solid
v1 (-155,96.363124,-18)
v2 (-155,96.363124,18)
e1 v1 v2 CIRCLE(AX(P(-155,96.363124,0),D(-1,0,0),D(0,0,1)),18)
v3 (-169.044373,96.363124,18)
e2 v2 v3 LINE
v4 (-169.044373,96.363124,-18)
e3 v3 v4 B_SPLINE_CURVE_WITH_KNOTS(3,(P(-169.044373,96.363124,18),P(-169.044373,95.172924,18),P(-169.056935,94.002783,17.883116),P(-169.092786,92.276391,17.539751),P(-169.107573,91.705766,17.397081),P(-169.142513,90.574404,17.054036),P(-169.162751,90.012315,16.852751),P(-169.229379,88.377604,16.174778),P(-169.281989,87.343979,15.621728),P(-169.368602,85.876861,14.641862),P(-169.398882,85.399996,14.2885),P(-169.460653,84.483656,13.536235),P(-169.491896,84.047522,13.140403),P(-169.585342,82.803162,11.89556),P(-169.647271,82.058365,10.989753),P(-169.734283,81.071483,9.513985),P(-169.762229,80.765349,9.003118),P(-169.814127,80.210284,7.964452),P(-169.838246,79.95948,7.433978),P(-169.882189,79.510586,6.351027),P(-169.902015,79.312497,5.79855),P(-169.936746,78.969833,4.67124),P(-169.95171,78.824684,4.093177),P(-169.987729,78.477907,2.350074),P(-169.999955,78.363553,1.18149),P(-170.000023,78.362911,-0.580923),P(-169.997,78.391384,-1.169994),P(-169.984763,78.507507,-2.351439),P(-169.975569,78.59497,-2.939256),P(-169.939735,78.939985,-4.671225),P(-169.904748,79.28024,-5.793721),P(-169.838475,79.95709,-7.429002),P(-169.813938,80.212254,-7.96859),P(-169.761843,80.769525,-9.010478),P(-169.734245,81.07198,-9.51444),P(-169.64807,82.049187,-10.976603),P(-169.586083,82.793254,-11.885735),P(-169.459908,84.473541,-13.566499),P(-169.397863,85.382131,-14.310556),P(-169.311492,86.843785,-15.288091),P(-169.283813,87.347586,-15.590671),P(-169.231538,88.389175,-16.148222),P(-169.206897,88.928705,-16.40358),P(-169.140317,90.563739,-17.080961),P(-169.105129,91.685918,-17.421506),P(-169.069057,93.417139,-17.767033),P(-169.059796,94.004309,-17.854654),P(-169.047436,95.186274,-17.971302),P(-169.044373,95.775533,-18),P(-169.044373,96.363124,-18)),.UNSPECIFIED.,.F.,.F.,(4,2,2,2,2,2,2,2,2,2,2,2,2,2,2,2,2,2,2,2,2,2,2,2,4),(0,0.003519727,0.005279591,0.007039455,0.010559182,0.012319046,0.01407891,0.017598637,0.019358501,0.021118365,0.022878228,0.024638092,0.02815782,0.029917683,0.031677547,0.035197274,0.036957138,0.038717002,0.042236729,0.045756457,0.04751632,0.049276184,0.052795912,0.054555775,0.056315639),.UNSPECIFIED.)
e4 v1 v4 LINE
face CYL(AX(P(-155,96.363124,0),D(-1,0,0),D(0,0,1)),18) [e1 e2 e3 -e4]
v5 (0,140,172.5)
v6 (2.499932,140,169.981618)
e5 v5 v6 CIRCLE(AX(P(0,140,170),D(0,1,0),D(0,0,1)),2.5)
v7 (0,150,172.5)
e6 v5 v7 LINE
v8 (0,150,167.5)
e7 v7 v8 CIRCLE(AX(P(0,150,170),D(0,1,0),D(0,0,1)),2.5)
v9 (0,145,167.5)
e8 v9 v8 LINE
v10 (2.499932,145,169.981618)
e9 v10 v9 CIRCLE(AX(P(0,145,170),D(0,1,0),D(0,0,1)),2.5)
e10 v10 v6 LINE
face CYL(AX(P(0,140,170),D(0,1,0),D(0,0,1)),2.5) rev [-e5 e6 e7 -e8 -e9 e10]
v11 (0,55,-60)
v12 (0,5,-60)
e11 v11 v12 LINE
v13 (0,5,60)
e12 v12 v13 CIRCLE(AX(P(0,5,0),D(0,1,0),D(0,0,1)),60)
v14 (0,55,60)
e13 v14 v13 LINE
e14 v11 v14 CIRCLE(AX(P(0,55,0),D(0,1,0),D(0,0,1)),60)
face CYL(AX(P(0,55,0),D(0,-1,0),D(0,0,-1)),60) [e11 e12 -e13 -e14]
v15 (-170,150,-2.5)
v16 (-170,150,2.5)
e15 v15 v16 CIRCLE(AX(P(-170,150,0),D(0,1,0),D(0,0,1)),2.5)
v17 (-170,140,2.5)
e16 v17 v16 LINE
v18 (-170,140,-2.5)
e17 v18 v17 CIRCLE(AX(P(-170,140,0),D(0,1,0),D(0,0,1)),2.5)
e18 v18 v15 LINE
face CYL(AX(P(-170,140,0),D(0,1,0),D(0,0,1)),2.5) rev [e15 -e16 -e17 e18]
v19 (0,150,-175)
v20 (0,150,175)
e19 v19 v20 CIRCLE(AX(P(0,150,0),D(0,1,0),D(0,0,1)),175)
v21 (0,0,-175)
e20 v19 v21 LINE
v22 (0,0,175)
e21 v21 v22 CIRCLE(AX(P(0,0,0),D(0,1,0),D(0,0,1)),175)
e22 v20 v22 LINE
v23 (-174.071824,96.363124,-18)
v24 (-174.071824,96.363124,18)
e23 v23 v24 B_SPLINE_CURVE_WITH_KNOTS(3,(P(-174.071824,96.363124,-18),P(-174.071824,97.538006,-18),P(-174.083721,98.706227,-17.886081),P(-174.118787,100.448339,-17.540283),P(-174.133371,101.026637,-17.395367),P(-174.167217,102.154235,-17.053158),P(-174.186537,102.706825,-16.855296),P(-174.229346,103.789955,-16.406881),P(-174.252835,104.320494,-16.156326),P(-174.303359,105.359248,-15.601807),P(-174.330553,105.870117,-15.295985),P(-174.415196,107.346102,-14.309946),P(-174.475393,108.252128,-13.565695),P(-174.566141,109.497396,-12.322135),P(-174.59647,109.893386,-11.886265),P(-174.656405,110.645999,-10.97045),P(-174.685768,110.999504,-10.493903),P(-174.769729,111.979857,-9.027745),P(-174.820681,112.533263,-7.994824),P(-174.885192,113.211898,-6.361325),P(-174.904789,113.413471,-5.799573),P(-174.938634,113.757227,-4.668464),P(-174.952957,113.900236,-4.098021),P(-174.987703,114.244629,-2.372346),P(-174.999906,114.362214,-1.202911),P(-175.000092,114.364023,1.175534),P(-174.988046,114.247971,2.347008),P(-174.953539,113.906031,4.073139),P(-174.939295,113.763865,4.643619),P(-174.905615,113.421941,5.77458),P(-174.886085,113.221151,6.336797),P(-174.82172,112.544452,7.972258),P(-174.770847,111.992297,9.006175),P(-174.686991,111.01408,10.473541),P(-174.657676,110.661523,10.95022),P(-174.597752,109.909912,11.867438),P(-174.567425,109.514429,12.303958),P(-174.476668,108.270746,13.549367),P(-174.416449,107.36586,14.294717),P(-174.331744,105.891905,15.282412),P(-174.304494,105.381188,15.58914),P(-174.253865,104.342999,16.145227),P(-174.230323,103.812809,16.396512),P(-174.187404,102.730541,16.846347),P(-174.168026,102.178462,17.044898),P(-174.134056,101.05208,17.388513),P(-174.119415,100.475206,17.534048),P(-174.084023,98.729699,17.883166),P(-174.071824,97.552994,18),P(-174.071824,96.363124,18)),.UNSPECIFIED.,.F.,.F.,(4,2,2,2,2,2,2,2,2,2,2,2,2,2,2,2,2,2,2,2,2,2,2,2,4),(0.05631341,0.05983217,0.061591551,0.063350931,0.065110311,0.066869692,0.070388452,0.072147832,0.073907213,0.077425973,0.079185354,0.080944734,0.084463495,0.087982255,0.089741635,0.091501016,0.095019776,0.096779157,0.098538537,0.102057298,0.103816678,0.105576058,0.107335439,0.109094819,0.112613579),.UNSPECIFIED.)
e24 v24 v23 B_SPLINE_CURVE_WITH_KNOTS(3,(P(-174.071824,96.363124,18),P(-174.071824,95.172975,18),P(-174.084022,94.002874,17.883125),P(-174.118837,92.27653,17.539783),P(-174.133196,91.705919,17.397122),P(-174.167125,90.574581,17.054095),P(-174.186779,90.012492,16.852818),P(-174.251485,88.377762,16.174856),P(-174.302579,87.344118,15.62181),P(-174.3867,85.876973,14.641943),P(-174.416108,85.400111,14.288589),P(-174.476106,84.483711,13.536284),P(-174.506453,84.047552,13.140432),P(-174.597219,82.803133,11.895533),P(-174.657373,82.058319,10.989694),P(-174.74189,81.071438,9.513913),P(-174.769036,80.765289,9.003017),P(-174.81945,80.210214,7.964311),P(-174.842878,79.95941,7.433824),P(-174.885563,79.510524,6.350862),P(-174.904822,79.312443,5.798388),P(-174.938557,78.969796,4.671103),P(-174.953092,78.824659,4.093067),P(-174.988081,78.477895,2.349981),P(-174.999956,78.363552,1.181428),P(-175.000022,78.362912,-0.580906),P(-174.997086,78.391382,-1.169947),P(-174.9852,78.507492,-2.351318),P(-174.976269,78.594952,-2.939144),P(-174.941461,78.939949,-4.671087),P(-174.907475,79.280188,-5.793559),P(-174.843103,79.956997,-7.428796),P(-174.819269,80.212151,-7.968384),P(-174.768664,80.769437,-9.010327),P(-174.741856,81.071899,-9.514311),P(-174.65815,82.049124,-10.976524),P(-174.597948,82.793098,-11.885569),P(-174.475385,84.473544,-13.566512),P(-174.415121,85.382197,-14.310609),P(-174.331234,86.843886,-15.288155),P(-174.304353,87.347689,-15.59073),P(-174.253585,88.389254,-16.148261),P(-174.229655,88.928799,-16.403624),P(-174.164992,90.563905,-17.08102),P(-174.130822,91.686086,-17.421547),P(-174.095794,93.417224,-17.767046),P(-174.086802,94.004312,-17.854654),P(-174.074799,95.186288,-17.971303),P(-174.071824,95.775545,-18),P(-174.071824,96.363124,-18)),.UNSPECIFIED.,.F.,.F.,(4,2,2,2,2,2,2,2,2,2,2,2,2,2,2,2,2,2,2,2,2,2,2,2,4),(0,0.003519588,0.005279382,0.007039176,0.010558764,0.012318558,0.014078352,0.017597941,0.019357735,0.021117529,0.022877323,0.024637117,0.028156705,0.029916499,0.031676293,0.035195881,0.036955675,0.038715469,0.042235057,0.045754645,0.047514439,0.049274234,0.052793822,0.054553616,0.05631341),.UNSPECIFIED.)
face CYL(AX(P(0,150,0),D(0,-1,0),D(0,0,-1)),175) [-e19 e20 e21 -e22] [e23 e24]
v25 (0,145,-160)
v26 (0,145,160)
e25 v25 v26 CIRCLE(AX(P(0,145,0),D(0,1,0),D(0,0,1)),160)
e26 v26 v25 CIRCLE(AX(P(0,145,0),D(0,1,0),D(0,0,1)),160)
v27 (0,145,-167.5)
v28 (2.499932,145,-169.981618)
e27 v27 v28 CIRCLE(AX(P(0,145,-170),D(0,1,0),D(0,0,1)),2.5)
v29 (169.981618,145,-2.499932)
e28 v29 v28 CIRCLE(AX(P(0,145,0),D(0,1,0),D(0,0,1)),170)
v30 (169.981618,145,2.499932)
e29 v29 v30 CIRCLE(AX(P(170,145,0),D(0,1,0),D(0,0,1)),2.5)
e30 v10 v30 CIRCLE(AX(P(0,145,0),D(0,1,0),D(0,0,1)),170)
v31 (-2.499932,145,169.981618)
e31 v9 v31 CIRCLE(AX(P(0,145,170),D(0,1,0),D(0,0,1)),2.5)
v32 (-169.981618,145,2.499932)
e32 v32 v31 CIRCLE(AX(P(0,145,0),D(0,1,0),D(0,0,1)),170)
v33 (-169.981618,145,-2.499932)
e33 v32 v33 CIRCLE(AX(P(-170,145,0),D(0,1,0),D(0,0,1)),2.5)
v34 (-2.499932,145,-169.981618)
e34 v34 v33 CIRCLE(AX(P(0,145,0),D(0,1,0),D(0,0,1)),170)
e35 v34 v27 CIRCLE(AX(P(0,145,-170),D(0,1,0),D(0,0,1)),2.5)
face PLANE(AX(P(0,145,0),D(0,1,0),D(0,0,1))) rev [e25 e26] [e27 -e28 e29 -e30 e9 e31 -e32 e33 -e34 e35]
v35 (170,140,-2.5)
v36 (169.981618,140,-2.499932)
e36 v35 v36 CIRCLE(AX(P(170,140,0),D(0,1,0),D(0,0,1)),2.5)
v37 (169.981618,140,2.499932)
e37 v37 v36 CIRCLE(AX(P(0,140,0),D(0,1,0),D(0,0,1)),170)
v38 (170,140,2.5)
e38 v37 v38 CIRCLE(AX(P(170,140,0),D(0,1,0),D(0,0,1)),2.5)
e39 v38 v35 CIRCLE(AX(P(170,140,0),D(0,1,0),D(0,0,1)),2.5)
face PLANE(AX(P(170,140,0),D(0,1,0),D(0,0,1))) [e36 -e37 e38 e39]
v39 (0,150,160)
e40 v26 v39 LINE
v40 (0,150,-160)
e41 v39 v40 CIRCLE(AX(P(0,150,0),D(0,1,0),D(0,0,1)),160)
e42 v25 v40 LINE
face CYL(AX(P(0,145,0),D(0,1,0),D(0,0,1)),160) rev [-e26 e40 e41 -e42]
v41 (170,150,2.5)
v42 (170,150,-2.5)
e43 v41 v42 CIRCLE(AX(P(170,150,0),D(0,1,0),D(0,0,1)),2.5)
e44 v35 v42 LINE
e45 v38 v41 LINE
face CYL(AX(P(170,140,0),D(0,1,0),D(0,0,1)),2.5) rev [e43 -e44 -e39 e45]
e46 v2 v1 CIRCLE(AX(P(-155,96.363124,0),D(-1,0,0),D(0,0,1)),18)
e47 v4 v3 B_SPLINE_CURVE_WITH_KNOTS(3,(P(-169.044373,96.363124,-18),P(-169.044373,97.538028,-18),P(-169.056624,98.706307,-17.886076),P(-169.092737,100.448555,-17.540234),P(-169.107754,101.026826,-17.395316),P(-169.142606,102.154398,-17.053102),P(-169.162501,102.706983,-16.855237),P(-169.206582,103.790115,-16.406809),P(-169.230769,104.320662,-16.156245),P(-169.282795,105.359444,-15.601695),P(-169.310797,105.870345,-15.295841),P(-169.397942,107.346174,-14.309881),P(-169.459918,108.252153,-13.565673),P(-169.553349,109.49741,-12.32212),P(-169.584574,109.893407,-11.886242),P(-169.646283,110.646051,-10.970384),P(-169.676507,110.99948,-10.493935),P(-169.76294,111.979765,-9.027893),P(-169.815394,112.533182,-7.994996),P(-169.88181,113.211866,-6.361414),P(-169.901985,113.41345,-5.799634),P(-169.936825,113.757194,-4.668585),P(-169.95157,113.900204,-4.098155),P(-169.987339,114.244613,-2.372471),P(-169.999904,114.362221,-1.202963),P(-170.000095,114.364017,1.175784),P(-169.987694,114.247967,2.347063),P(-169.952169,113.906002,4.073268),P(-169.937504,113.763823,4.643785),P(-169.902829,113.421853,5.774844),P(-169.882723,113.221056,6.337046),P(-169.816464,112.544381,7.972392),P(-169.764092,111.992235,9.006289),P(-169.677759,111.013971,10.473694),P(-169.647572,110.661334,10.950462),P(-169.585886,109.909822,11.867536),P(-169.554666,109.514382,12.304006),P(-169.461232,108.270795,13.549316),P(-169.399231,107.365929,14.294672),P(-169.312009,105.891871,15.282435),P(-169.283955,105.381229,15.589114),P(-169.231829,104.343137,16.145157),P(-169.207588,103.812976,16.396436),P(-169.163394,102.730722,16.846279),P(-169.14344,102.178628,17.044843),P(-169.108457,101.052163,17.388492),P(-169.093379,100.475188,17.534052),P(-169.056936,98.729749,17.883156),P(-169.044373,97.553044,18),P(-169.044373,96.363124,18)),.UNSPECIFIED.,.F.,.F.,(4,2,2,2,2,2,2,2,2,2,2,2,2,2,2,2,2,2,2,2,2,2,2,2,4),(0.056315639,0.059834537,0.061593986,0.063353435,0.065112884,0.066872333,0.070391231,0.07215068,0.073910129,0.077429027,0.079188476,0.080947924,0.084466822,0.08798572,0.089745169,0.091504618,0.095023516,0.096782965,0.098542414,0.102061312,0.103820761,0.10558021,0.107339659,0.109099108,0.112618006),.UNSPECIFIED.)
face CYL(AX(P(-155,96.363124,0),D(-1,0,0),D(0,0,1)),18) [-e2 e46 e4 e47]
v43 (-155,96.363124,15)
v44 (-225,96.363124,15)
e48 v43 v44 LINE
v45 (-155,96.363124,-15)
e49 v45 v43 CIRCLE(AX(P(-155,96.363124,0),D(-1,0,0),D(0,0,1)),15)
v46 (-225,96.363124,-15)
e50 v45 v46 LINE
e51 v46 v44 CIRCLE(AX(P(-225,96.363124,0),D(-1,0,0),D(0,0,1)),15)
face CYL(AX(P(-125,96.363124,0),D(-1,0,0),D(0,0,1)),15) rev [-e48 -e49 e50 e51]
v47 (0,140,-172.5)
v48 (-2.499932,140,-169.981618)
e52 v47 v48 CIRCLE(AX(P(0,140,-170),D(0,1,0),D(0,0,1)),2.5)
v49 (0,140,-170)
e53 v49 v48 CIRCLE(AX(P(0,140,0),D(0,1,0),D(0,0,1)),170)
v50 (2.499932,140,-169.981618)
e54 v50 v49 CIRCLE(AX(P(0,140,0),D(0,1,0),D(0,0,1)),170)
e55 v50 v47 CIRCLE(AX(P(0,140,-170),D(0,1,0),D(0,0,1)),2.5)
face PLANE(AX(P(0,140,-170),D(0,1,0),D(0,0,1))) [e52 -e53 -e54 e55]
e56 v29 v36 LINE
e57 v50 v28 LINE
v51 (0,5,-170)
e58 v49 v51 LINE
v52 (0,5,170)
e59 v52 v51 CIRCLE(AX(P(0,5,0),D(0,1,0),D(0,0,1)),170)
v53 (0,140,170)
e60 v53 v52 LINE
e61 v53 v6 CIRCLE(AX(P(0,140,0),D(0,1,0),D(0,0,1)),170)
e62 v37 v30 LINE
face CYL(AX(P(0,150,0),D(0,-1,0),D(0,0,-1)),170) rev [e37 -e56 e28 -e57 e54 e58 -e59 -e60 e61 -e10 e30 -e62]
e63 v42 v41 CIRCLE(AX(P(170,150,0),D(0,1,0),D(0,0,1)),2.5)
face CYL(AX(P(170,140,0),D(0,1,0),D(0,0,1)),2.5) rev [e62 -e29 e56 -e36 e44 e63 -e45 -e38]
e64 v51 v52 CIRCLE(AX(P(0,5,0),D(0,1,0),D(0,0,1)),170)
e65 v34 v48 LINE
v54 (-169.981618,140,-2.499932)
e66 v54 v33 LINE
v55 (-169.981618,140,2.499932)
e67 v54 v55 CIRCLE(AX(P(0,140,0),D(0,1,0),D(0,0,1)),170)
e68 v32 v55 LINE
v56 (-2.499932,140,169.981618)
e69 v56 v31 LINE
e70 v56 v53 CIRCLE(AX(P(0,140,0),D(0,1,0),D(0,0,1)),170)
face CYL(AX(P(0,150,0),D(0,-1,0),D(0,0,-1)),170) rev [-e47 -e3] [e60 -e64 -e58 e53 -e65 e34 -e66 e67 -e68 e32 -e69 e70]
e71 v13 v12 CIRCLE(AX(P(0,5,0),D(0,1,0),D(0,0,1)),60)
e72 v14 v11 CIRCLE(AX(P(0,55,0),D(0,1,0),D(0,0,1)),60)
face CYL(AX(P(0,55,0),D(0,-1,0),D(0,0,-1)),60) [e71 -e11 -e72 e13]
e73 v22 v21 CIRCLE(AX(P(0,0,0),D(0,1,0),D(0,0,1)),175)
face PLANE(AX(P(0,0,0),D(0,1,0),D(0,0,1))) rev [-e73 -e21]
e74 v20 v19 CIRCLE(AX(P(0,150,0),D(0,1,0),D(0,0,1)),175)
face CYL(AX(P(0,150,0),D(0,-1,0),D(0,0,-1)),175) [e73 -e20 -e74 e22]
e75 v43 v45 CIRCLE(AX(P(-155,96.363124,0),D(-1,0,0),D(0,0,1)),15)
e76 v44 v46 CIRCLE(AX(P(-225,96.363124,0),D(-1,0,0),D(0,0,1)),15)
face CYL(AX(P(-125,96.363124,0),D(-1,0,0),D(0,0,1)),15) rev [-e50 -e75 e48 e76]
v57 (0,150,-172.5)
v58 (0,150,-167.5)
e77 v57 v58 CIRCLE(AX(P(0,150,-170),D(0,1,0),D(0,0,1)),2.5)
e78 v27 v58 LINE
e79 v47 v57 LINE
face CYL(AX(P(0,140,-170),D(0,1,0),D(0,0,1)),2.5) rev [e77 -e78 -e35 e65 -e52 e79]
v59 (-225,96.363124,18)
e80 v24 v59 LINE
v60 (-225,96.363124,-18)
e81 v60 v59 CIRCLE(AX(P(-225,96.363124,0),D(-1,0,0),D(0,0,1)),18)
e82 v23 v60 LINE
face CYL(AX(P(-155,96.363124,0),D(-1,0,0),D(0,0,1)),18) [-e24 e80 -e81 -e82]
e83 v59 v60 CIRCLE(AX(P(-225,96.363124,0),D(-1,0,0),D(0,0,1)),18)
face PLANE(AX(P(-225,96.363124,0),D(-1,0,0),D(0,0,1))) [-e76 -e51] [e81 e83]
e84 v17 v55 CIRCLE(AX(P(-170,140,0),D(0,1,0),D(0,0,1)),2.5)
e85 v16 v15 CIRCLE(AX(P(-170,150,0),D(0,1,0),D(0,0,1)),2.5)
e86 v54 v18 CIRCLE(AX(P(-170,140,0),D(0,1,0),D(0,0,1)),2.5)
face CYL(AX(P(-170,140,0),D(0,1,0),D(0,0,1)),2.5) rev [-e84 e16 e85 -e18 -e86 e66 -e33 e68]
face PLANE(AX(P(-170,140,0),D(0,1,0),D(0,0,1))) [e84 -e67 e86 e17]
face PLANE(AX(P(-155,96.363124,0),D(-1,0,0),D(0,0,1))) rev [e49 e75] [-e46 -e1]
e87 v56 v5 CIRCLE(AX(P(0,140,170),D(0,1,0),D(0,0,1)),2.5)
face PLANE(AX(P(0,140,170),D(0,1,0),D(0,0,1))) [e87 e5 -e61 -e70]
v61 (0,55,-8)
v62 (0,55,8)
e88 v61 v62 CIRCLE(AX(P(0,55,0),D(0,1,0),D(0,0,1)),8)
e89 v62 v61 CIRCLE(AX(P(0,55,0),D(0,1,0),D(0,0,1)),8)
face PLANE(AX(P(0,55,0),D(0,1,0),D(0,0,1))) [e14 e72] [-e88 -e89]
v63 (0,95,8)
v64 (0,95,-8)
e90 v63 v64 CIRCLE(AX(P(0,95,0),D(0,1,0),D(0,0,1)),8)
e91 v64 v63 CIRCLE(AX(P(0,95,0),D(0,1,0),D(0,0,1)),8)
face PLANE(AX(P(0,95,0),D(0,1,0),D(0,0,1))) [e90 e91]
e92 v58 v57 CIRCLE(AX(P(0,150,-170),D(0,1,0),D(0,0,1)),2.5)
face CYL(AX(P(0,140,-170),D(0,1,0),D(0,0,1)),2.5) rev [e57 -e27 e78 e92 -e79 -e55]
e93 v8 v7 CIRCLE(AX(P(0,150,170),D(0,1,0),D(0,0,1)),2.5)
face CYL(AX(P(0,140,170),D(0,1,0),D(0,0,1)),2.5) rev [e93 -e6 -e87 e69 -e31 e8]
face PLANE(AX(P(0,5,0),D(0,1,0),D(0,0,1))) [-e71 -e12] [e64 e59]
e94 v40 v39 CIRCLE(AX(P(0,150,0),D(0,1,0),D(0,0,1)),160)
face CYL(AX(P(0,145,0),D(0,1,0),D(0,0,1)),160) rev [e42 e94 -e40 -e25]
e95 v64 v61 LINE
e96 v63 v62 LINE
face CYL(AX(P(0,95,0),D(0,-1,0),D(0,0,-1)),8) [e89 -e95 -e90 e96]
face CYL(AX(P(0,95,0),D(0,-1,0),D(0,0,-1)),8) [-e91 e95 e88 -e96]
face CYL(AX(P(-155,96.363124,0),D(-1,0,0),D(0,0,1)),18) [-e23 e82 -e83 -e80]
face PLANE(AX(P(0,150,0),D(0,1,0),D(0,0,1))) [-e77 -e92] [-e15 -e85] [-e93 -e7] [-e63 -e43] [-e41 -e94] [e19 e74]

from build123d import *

# Parameters (mm, degrees)
SKETCH1_R                = 175
BOSS_EXTRUDE2_DEPTH      = 150
SHELL2_T                 = -5
SKETCH2_R                = 60
BOSS_EXTRUDE3_DEPTH      = 50
SKETCH_3_3_R             = 15
CUT_EXTRUDE1_DEPTH       = 50
BOSS_EXTRUDE5_DEPTH      = 50
BOSS_EXTRUDE5_DEPTH_BACK = 20
SKETCH_3_3_2_R           = 18
SKETCH_3_3_2_R_2         = 15
SKETCH5_R                = 8
BOSS_EXTRUDE6_DEPTH      = 40
BOSS_EXTRUDE7_START      = -5
SKETCH6_R                = 170
SKETCH6_R_2              = 160
BOSS_EXTRUDE7_DEPTH      = 5
SKETCH7_R                = 2.5
CUT_EXTRUDE2_DEPTH       = 10


with BuildPart() as part:
    # Sketch1 → Boss-Extrude2 (new body)
    with BuildSketch(Plane(origin=(0, 0, 0), x_dir=(1, 0, 0), z_dir=(0, 1, 0))):
        with Locations(Location((0, 0, 0), (0, 0, 270))):
            Circle(SKETCH1_R)
    extrude(amount=BOSS_EXTRUDE2_DEPTH)

    # Shell2
    shell2_openings = [part.faces().sort_by_distance(p)[0] for p in [
        (0, 150, 0),
    ]]
    offset(amount=SHELL2_T, openings=shell2_openings, kind=Kind.INTERSECTION)

    # Sketch2 → Boss-Extrude3 (add)
    with BuildSketch(Plane(origin=(0, 5, 0), x_dir=(1, 0, 0), z_dir=(0, 1, 0))):
        with Locations(Location((0, 0, 0), (0, 0, 270))):
            Circle(SKETCH2_R)
    extrude(amount=BOSS_EXTRUDE3_DEPTH)

    # Sketch 3_3 → Cut-Extrude1 (cut)
    with BuildSketch(Plane.ZY.offset(175)):
        with Locations((0, 96.363123984)):
            Circle(SKETCH_3_3_R)
    extrude(amount=-CUT_EXTRUDE1_DEPTH, mode=Mode.SUBTRACT)

    # Sketch 3_3 2 → Boss-Extrude5 (add, two sides: drawn at the far end of the back side and taken through both)
    with BuildSketch(Plane.ZY.offset(175).offset(-BOSS_EXTRUDE5_DEPTH_BACK)):
        with Locations((0, 96.363123984)):
            Circle(SKETCH_3_3_2_R)
        with Locations((0, 96.363123984)):
            Circle(SKETCH_3_3_2_R_2, mode=Mode.SUBTRACT)
    extrude(amount=BOSS_EXTRUDE5_DEPTH + BOSS_EXTRUDE5_DEPTH_BACK)

    # Sketch5 → Boss-Extrude6 (add)
    with BuildSketch(Plane(origin=(0, 55, 0), x_dir=(1, 0, 0), z_dir=(0, 1, 0))):
        with Locations(Location((0, 0, 0), (0, 0, 270))):
            Circle(SKETCH5_R)
    extrude(amount=BOSS_EXTRUDE6_DEPTH)

    # Sketch6 → Boss-Extrude7 (add)
    with BuildSketch(Plane(origin=(0, 150, 0), x_dir=(1, 0, 0), z_dir=(0, 1, 0)).offset(BOSS_EXTRUDE7_START)):
        with Locations(Location((0, 0, 0), (0, 0, 270))):
            Circle(SKETCH6_R)
        with Locations(Location((0, 0, 0), (0, 0, 270))):
            Circle(SKETCH6_R_2, mode=Mode.SUBTRACT)
    extrude(amount=BOSS_EXTRUDE7_DEPTH)

    # Sketch7 → Cut-Extrude2 (cut)
    with BuildSketch(Plane(origin=(0, 150, 0), x_dir=(1, 0, 0), z_dir=(0, 1, 0))):
        with Locations(Location((0, -170, 0), (0, 0, 270))):
            Circle(SKETCH7_R)
        with Locations(Location((-170, 0, 0), (0, 0, 270))):
            Circle(SKETCH7_R)
        with Locations(Location((0, 170, 0), (0, 0, 270))):
            Circle(SKETCH7_R)
        with Locations(Location((170, 0, 0), (0, 0, 270))):
            Circle(SKETCH7_R)
    extrude(amount=-CUT_EXTRUDE2_DEPTH, mode=Mode.SUBTRACT)


solid = part.part
